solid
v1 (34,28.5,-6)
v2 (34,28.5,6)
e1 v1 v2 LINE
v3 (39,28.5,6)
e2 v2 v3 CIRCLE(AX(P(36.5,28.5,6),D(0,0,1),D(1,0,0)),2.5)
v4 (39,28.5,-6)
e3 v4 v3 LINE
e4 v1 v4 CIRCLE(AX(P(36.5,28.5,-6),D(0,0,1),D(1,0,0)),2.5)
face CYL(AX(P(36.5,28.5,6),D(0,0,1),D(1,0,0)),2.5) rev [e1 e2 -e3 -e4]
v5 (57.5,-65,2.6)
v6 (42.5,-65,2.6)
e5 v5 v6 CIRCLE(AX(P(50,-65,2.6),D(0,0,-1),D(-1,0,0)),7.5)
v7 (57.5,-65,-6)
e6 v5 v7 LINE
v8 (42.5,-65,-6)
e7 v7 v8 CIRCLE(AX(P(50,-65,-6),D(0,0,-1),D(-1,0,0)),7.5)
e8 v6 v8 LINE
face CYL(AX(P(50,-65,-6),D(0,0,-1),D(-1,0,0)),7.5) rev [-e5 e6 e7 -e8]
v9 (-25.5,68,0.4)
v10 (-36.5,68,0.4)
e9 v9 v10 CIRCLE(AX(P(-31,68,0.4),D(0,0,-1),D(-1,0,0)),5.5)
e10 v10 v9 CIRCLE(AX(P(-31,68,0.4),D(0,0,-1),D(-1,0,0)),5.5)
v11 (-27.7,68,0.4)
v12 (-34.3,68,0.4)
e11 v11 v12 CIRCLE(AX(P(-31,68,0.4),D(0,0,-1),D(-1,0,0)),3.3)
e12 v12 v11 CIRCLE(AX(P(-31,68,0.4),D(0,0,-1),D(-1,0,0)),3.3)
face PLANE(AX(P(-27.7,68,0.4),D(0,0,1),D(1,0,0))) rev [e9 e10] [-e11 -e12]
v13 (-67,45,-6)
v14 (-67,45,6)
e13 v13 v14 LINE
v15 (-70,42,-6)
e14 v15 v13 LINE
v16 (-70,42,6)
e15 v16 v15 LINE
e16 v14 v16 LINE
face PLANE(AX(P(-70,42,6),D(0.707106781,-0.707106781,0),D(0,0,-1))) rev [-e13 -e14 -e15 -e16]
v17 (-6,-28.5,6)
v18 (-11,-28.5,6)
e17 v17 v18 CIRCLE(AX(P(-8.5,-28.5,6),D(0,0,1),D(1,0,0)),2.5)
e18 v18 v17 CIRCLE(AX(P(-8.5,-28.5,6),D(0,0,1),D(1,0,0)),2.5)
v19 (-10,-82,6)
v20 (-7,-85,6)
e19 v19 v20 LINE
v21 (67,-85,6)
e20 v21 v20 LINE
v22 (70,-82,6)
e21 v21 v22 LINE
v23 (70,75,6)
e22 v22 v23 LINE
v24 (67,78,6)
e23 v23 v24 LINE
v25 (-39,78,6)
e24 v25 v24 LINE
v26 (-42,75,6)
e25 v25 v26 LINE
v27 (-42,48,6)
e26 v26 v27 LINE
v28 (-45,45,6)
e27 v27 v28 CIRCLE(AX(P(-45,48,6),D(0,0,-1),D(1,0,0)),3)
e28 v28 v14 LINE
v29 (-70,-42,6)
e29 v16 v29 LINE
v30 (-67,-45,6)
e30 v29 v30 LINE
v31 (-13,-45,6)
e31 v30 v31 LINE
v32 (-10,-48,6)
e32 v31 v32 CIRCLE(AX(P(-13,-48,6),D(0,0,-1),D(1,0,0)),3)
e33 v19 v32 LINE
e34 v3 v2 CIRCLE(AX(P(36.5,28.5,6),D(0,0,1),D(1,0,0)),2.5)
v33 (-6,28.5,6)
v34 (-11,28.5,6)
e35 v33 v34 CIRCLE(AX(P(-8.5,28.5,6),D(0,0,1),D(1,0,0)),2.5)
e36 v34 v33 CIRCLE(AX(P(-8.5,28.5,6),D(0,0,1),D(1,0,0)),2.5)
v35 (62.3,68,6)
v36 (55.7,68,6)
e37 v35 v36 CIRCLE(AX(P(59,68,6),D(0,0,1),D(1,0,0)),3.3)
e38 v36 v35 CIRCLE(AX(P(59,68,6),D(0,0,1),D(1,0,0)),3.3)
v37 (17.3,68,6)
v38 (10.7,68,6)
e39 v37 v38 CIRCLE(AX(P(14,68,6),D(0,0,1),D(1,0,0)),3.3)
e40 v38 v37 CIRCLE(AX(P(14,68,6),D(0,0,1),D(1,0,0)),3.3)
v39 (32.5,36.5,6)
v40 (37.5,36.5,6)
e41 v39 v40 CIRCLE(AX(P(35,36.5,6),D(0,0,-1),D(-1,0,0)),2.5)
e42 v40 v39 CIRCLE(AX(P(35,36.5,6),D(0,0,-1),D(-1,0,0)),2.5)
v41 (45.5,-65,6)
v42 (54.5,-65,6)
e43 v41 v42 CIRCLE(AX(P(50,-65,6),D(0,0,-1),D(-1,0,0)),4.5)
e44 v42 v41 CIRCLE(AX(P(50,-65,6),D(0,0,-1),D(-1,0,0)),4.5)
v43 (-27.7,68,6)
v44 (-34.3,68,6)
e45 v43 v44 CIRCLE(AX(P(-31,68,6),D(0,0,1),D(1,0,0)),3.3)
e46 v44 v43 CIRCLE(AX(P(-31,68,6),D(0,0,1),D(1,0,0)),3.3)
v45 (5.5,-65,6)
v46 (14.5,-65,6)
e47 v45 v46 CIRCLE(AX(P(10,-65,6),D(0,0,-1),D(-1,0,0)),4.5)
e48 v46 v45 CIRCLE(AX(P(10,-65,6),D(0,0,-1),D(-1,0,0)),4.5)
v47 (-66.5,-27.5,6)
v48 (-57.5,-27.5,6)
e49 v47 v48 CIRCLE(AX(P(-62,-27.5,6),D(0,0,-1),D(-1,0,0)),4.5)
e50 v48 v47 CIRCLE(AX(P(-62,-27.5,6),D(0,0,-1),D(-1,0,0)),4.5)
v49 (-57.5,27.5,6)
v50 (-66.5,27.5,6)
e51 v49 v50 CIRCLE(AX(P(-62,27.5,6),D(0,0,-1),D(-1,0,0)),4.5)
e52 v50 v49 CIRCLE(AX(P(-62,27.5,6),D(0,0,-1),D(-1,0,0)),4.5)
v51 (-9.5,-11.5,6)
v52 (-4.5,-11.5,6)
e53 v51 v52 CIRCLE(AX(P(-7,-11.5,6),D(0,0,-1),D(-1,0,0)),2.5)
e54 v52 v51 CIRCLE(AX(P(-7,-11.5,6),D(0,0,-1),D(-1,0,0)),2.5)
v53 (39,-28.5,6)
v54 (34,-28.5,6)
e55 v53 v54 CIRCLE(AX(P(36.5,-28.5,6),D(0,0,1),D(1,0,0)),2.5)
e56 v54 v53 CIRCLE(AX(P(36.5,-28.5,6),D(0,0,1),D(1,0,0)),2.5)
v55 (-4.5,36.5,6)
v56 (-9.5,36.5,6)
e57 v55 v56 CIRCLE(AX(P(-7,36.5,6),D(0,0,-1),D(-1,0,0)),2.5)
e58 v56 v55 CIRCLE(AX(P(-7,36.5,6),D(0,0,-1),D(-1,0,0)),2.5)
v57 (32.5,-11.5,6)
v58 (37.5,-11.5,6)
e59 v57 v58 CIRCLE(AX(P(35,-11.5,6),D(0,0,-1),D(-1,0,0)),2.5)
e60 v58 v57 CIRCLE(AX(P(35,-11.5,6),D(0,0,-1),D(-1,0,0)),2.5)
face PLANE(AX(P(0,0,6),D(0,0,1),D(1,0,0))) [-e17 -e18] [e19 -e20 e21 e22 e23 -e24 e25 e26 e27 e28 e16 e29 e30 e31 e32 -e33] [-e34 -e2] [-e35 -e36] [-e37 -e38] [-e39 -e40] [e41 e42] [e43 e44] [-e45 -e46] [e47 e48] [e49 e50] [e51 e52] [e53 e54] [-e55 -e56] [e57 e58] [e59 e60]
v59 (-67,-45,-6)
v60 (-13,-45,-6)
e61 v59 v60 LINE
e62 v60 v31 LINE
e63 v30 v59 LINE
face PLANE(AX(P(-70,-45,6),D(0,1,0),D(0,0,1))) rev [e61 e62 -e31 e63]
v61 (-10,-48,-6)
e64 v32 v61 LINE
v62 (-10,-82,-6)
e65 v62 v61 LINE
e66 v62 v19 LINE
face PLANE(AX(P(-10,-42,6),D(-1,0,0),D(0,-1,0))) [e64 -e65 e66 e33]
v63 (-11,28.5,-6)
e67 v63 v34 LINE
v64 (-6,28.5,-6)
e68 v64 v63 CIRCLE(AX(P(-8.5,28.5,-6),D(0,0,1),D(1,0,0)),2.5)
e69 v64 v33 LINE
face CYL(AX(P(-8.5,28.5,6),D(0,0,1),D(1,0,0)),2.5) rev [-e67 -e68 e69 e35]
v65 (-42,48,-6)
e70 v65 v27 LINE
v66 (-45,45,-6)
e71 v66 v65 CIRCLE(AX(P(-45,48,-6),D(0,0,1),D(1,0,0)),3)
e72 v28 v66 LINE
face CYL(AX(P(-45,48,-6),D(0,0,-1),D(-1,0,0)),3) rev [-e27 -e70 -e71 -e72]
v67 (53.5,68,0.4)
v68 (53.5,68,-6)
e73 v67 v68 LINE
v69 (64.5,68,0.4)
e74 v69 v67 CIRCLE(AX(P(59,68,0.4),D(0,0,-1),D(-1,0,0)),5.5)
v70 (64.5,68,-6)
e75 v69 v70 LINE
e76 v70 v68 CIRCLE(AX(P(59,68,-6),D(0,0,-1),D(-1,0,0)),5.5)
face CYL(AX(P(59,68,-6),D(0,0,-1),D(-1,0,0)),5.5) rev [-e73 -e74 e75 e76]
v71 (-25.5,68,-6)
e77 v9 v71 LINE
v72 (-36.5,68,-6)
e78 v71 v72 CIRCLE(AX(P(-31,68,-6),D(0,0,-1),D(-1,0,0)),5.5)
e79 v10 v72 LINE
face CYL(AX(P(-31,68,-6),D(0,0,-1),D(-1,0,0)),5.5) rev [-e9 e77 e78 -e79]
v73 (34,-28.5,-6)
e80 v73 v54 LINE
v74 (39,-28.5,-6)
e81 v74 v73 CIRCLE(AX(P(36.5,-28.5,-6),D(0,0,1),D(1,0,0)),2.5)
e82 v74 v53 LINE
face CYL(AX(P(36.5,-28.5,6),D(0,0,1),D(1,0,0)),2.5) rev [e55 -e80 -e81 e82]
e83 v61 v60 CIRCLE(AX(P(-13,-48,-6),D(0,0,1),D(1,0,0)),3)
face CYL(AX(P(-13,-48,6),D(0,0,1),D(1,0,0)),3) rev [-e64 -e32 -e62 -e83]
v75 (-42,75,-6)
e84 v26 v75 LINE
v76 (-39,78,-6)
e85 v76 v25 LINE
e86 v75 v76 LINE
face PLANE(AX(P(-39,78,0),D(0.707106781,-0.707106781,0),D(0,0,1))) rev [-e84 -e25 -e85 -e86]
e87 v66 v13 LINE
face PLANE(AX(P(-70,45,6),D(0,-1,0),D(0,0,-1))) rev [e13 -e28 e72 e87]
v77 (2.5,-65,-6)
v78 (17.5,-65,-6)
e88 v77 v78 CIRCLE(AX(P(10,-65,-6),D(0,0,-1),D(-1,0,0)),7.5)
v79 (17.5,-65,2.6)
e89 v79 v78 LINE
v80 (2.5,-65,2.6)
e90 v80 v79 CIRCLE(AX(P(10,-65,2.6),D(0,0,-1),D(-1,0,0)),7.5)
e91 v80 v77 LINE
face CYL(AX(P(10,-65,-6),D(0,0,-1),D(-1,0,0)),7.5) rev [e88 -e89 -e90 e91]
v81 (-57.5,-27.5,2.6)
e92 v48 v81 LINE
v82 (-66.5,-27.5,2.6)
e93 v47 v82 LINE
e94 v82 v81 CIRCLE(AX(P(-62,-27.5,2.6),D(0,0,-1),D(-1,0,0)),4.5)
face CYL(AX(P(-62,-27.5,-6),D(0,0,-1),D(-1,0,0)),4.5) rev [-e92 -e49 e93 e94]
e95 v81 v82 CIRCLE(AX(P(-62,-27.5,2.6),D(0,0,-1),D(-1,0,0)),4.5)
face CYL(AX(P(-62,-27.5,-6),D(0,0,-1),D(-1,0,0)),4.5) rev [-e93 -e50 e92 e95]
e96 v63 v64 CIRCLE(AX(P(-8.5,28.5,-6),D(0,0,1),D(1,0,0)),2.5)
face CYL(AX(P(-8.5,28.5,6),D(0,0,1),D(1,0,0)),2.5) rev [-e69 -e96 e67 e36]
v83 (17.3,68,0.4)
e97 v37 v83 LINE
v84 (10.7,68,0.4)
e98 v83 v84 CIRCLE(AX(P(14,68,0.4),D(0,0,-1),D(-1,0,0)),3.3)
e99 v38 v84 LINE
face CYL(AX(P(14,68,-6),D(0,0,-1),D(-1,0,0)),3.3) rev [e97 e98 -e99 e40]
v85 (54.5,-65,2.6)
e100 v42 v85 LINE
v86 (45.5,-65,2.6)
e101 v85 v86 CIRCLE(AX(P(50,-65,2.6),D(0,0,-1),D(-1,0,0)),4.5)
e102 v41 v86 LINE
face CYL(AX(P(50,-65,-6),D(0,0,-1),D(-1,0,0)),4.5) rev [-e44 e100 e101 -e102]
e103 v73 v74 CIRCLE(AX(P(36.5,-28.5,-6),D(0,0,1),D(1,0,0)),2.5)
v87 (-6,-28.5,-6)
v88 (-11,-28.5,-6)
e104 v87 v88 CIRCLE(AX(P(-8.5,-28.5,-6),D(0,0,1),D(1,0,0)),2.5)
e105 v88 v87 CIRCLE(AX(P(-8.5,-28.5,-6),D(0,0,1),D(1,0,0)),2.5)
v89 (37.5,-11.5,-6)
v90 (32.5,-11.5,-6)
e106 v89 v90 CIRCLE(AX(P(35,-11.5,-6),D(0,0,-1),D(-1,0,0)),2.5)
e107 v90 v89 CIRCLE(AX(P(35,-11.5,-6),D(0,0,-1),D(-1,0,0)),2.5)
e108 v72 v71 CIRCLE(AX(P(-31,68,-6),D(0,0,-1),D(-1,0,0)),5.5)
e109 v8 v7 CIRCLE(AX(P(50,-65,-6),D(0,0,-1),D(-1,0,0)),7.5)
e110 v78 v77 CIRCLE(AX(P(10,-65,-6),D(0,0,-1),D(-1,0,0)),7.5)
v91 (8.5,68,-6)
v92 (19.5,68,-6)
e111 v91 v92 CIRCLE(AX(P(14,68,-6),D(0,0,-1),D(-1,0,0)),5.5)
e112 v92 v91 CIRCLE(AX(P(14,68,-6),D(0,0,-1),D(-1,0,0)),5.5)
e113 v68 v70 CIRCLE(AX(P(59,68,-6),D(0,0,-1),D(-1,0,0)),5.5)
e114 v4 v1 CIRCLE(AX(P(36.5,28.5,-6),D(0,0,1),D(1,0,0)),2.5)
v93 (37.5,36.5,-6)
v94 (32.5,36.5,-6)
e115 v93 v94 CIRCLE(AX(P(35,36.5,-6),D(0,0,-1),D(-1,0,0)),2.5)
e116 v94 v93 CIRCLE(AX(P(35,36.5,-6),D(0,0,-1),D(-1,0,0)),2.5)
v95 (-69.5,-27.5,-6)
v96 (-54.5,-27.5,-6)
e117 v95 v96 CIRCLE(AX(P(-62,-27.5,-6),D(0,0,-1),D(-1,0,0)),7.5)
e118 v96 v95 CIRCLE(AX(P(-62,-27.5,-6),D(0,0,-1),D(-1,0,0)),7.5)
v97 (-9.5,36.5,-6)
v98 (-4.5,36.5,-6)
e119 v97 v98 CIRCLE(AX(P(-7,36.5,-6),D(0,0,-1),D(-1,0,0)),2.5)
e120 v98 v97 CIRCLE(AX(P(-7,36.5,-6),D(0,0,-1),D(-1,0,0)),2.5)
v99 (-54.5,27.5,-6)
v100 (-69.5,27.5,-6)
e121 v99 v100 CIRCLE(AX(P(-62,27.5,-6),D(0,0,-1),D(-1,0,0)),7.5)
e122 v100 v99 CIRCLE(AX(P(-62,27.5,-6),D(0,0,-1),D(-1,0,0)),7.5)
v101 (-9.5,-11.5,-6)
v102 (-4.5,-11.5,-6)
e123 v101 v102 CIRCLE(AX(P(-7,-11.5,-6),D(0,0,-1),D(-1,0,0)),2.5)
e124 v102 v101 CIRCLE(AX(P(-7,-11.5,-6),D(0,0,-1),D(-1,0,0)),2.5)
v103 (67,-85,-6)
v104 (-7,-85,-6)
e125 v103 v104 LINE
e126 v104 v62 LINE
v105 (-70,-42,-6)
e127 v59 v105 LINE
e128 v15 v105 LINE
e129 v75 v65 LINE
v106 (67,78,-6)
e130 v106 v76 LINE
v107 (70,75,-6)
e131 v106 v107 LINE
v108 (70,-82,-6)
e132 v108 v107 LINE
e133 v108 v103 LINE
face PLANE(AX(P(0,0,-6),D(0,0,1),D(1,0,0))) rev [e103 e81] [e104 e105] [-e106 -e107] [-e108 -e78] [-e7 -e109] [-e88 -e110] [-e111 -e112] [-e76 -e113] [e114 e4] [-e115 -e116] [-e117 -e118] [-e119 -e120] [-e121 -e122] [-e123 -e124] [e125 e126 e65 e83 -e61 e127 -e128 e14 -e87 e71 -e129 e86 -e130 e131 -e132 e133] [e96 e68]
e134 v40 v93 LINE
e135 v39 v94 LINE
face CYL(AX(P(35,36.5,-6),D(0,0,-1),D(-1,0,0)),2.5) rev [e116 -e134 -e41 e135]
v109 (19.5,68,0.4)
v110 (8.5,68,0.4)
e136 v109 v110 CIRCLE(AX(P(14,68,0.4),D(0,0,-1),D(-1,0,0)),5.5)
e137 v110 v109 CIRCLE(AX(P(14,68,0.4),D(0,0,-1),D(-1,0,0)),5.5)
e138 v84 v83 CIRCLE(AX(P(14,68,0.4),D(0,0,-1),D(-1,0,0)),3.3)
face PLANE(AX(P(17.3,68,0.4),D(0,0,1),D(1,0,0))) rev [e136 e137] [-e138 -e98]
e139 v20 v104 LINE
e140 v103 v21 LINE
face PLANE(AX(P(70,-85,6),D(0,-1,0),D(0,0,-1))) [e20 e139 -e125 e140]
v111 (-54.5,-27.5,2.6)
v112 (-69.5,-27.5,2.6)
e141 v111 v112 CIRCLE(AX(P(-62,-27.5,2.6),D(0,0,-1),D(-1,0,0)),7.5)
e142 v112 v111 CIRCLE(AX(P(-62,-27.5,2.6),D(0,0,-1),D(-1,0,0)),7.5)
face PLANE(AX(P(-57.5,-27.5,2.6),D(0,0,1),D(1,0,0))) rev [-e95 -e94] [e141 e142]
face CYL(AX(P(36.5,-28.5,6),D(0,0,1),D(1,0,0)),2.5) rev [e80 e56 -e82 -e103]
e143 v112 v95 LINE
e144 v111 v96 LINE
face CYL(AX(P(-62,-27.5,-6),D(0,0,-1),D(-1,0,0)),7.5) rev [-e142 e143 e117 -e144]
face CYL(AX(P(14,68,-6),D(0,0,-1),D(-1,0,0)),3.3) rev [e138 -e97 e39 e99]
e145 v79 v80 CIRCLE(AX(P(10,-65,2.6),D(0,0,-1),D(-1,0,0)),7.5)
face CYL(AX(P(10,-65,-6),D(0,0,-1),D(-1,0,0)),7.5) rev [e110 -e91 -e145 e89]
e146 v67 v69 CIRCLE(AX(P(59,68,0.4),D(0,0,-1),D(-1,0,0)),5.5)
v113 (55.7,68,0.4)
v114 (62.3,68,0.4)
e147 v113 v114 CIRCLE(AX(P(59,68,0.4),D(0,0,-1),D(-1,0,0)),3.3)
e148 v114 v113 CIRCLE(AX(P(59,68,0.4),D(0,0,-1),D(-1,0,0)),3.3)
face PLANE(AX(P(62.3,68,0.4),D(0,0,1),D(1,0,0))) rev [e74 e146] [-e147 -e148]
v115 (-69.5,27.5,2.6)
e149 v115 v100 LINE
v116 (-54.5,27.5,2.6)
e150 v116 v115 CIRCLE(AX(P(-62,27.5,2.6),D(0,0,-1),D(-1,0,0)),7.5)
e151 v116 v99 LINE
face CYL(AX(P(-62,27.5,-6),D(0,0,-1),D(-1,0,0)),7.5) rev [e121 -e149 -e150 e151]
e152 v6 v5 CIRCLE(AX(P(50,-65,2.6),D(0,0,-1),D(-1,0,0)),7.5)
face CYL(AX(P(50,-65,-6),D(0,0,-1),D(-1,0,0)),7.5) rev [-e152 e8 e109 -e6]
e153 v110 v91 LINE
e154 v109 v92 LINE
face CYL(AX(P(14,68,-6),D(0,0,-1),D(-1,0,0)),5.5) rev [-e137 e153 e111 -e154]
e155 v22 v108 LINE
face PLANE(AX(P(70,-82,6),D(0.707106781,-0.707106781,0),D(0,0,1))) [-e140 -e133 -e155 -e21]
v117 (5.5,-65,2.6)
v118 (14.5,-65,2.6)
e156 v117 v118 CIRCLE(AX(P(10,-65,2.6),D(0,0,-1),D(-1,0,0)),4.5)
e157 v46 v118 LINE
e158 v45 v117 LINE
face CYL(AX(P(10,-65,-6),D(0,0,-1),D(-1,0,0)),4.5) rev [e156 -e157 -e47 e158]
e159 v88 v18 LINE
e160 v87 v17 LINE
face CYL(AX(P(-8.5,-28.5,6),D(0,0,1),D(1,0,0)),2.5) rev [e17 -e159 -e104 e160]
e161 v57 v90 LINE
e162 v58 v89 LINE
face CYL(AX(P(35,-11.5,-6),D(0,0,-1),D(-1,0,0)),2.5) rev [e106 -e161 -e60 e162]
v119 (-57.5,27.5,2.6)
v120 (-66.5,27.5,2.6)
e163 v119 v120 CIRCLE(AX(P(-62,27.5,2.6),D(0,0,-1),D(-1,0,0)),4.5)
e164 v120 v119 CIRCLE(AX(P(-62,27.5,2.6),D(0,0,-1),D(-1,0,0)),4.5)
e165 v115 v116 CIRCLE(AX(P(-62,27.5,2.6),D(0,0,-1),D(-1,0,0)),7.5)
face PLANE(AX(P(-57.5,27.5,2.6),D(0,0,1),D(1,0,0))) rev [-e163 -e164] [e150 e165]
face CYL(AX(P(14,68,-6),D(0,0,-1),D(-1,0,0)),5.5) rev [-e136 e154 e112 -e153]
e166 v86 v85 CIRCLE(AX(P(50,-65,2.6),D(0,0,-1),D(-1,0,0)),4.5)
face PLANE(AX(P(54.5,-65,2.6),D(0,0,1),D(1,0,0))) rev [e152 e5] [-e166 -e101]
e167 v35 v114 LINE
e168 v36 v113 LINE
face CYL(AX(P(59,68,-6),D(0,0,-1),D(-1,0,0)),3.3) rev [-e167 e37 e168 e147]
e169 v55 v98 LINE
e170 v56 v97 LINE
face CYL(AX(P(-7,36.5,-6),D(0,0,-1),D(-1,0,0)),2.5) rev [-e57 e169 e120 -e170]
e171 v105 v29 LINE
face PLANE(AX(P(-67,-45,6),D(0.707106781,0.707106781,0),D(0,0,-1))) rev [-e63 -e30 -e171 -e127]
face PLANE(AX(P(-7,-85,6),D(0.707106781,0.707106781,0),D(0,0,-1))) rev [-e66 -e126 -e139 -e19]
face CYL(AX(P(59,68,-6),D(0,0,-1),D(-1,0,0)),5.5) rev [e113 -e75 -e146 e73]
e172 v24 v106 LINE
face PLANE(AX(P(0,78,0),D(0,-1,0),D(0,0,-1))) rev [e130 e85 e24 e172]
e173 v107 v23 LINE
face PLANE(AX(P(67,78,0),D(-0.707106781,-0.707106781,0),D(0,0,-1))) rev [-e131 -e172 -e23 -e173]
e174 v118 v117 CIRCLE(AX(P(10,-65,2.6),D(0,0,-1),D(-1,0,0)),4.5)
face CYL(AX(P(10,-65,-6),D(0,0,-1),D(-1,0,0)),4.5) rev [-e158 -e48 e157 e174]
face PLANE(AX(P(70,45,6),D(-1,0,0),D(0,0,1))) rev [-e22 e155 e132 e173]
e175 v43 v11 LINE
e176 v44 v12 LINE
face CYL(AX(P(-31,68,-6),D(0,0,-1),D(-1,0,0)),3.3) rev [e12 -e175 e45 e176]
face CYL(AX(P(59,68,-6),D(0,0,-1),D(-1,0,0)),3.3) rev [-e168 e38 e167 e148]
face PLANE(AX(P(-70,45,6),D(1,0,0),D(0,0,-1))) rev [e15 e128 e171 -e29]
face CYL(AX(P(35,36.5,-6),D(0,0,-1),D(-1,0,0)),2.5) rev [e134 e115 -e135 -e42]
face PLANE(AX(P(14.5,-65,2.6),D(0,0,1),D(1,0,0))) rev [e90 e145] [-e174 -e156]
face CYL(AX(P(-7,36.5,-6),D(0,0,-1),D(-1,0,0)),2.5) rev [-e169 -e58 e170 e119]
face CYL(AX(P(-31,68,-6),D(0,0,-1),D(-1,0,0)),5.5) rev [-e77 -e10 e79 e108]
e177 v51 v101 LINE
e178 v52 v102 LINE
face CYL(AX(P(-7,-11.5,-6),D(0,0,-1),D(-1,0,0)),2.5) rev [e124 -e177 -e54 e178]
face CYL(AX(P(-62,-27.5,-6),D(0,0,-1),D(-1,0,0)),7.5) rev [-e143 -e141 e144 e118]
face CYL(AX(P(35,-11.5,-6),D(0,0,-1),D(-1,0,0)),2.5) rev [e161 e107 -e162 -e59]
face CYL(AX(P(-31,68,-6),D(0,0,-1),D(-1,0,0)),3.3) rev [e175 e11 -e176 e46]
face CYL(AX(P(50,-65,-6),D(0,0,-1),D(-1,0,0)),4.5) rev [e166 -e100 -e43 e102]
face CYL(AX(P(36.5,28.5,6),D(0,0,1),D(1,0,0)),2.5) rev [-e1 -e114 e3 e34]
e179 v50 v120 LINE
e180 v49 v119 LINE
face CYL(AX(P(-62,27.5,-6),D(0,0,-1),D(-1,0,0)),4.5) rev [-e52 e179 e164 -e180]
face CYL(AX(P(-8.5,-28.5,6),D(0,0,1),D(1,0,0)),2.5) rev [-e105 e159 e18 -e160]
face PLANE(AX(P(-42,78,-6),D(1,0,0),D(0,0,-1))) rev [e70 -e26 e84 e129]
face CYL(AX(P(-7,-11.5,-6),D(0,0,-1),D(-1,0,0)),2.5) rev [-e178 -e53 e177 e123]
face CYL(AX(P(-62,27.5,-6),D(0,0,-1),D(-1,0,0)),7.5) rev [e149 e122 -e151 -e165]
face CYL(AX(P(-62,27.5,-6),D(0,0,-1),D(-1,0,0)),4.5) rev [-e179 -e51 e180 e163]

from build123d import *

# Parameters (mm, degrees)
SKETCH_1_W                   = 140
SKETCH_1_H                   = 90
EXTRUDE_1_DEPTH              = 6
HOLE_WIZARD_M6_2_D           = 5
PATTERN_LINEAR_3_COUNT       = 2
PATTERN_LINEAR_3_PITCH       = 45
PATTERN_LINEAR_3_COPY_1_D    = 5
HOLE_WIZARD_M8_1_D           = 9
HOLE_WIZARD_M8_1_CBORE_D     = 15
HOLE_WIZARD_M8_1_CBORE_DEPTH = 8.6
SKETCH_11_W                  = 112
SKETCH_11_H                  = 12
EXTRUDE_2_DEPTH              = 33
FILLET_1_R                   = 3
CHAMFER_2_SIZE               = 3
HOLE_WIZARD_M6_1_D           = 6.6
HOLE_WIZARD_M6_1_DEPTH       = 15
HOLE_WIZARD_M6_1_CBORE_D     = 11
HOLE_WIZARD_M6_1_CBORE_DEPTH = 6.4
HOLE_WIZARD_M6_1_TIP         = 1.982840043
HOLE_WIZARD_M6_3_D           = 5
SKETCH_16_W                  = 80
SKETCH_16_H                  = 43
EXTRUDE_3_DEPTH              = 12
CHAMFER_3_SIZE               = 3
FILLET_2_R                   = 3
HOLE_WIZARD_M8_2_D           = 9
HOLE_WIZARD_M8_2_CBORE_D     = 15
HOLE_WIZARD_M8_2_CBORE_DEPTH = 8.6


with BuildPart() as part:
    # 草图1 → 凸台-拉伸1 (new, symmetric)
    with BuildSketch(Plane.XY):
        Rectangle(SKETCH_1_W, SKETCH_1_H)
    extrude(amount=EXTRUDE_1_DEPTH, both=True)

    # M6 螺纹孔2 (through all)
    with Locations(Plane.XY.offset(6)):
        with Locations((36.5, 28.5)):
            hole_wizard_m6_2 = Hole(HOLE_WIZARD_M6_2_D / 2)

    # 镜向1: M6 螺纹孔2 across plane
    add(hole_wizard_m6_2.mirror(Plane.ZX), mode=Mode.SUBTRACT)

    # 阵列(线性)3: M6 螺纹孔2 ×2
    with Locations(*[(-i * PATTERN_LINEAR_3_PITCH, 0, 0) for i in range(1, PATTERN_LINEAR_3_COUNT)]):
        add(hole_wizard_m6_2, mode=Mode.SUBTRACT)

    # 阵列(线性)3 copy 1 (through all)
    with Locations(Plane(origin=(-45, 0, 6), x_dir=(1, 0, 0), z_dir=(0, 0, 1))):
        with Locations((36.5, -28.5)):
            Hole(PATTERN_LINEAR_3_COPY_1_D / 2)

    # M8 六角凹头螺钉的柱形沉头孔1 (through all)
    with Locations(Plane(origin=(0, 0, -6), x_dir=(-1, 0, 0), z_dir=(0, 0, -1))):
        with Locations((62, 27.5), (62, -27.5)):
            CounterBoreHole(HOLE_WIZARD_M8_1_D / 2, HOLE_WIZARD_M8_1_CBORE_D / 2, HOLE_WIZARD_M8_1_CBORE_DEPTH)

    # 草图11 → 凸台-拉伸2 (add)
    with BuildSketch(Plane(origin=(0, 45, 0), x_dir=(1, 0, 0), z_dir=(0, 1, 0))):
        with Locations((14, 0)):
            Rectangle(SKETCH_11_W, SKETCH_11_H)
    extrude(amount=EXTRUDE_2_DEPTH)

    # 圆角1
    fillet_1_edges = [part.edges().sort_by_distance(p)[0] for p in [
        (-42, 45, 0),
    ]]
    fillet(fillet_1_edges, radius=FILLET_1_R)

    # 倒角2
    chamfer_2_edges = [part.edges().sort_by_distance(p)[0] for p in [
        (70, -45, 0),
        (-70, -45, 0),
        (-70, 45, 0),
        (-42, 78, 0),
        (70, 78, 0),
    ]]
    chamfer(chamfer_2_edges, length=CHAMFER_2_SIZE)

    # M6 六角凹头螺钉的柱形沉头孔1
    with Locations(Plane(origin=(0, 0, -6), x_dir=(-1, 0, 0), z_dir=(0, 0, -1))):
        with Locations((-59, 68), (-14, 68), (31, 68)):
            CounterBoreHole(HOLE_WIZARD_M6_1_D / 2, HOLE_WIZARD_M6_1_CBORE_D / 2, HOLE_WIZARD_M6_1_CBORE_DEPTH, depth=HOLE_WIZARD_M6_1_DEPTH)
            with Locations((0, 0, -(HOLE_WIZARD_M6_1_DEPTH + HOLE_WIZARD_M6_1_TIP / 2))):  # 118° drill point
                Cone(0, HOLE_WIZARD_M6_1_D / 2, HOLE_WIZARD_M6_1_TIP, mode=Mode.SUBTRACT)

    # M6 螺纹孔3 (through all)
    with Locations(Plane(origin=(0, 0, -6), x_dir=(-1, 0, 0), z_dir=(0, 0, -1))):
        with Locations((7, 36.5), (-35, 36.5), (7, -11.5), (-35, -11.5)):
            Hole(HOLE_WIZARD_M6_3_D / 2)

    # 草图16 → 凸台-拉伸3 (add)
    with BuildSketch(Plane(origin=(0, 0, -6), x_dir=(-1, 0, 0), z_dir=(0, 0, -1))):
        with Locations((-30, -63.5)):
            Rectangle(SKETCH_16_W, SKETCH_16_H)
    extrude(amount=-EXTRUDE_3_DEPTH)

    # 倒角3
    chamfer_3_edges = [part.edges().sort_by_distance(p)[0] for p in [
        (70, -85, 0),
        (-10, -85, 0),
    ]]
    chamfer(chamfer_3_edges, length=CHAMFER_3_SIZE)

    # 圆角2
    fillet_2_edges = [part.edges().sort_by_distance(p)[0] for p in [
        (-10, -45, 0),
    ]]
    fillet(fillet_2_edges, radius=FILLET_2_R)

    # M8 六角凹头螺钉的柱形沉头孔2 (through all)
    with Locations(Plane(origin=(0, 0, -6), x_dir=(-1, 0, 0), z_dir=(0, 0, -1))):
        with Locations((-50, -65), (-10, -65)):
            CounterBoreHole(HOLE_WIZARD_M8_2_D / 2, HOLE_WIZARD_M8_2_CBORE_D / 2, HOLE_WIZARD_M8_2_CBORE_DEPTH)


solid = part.part
